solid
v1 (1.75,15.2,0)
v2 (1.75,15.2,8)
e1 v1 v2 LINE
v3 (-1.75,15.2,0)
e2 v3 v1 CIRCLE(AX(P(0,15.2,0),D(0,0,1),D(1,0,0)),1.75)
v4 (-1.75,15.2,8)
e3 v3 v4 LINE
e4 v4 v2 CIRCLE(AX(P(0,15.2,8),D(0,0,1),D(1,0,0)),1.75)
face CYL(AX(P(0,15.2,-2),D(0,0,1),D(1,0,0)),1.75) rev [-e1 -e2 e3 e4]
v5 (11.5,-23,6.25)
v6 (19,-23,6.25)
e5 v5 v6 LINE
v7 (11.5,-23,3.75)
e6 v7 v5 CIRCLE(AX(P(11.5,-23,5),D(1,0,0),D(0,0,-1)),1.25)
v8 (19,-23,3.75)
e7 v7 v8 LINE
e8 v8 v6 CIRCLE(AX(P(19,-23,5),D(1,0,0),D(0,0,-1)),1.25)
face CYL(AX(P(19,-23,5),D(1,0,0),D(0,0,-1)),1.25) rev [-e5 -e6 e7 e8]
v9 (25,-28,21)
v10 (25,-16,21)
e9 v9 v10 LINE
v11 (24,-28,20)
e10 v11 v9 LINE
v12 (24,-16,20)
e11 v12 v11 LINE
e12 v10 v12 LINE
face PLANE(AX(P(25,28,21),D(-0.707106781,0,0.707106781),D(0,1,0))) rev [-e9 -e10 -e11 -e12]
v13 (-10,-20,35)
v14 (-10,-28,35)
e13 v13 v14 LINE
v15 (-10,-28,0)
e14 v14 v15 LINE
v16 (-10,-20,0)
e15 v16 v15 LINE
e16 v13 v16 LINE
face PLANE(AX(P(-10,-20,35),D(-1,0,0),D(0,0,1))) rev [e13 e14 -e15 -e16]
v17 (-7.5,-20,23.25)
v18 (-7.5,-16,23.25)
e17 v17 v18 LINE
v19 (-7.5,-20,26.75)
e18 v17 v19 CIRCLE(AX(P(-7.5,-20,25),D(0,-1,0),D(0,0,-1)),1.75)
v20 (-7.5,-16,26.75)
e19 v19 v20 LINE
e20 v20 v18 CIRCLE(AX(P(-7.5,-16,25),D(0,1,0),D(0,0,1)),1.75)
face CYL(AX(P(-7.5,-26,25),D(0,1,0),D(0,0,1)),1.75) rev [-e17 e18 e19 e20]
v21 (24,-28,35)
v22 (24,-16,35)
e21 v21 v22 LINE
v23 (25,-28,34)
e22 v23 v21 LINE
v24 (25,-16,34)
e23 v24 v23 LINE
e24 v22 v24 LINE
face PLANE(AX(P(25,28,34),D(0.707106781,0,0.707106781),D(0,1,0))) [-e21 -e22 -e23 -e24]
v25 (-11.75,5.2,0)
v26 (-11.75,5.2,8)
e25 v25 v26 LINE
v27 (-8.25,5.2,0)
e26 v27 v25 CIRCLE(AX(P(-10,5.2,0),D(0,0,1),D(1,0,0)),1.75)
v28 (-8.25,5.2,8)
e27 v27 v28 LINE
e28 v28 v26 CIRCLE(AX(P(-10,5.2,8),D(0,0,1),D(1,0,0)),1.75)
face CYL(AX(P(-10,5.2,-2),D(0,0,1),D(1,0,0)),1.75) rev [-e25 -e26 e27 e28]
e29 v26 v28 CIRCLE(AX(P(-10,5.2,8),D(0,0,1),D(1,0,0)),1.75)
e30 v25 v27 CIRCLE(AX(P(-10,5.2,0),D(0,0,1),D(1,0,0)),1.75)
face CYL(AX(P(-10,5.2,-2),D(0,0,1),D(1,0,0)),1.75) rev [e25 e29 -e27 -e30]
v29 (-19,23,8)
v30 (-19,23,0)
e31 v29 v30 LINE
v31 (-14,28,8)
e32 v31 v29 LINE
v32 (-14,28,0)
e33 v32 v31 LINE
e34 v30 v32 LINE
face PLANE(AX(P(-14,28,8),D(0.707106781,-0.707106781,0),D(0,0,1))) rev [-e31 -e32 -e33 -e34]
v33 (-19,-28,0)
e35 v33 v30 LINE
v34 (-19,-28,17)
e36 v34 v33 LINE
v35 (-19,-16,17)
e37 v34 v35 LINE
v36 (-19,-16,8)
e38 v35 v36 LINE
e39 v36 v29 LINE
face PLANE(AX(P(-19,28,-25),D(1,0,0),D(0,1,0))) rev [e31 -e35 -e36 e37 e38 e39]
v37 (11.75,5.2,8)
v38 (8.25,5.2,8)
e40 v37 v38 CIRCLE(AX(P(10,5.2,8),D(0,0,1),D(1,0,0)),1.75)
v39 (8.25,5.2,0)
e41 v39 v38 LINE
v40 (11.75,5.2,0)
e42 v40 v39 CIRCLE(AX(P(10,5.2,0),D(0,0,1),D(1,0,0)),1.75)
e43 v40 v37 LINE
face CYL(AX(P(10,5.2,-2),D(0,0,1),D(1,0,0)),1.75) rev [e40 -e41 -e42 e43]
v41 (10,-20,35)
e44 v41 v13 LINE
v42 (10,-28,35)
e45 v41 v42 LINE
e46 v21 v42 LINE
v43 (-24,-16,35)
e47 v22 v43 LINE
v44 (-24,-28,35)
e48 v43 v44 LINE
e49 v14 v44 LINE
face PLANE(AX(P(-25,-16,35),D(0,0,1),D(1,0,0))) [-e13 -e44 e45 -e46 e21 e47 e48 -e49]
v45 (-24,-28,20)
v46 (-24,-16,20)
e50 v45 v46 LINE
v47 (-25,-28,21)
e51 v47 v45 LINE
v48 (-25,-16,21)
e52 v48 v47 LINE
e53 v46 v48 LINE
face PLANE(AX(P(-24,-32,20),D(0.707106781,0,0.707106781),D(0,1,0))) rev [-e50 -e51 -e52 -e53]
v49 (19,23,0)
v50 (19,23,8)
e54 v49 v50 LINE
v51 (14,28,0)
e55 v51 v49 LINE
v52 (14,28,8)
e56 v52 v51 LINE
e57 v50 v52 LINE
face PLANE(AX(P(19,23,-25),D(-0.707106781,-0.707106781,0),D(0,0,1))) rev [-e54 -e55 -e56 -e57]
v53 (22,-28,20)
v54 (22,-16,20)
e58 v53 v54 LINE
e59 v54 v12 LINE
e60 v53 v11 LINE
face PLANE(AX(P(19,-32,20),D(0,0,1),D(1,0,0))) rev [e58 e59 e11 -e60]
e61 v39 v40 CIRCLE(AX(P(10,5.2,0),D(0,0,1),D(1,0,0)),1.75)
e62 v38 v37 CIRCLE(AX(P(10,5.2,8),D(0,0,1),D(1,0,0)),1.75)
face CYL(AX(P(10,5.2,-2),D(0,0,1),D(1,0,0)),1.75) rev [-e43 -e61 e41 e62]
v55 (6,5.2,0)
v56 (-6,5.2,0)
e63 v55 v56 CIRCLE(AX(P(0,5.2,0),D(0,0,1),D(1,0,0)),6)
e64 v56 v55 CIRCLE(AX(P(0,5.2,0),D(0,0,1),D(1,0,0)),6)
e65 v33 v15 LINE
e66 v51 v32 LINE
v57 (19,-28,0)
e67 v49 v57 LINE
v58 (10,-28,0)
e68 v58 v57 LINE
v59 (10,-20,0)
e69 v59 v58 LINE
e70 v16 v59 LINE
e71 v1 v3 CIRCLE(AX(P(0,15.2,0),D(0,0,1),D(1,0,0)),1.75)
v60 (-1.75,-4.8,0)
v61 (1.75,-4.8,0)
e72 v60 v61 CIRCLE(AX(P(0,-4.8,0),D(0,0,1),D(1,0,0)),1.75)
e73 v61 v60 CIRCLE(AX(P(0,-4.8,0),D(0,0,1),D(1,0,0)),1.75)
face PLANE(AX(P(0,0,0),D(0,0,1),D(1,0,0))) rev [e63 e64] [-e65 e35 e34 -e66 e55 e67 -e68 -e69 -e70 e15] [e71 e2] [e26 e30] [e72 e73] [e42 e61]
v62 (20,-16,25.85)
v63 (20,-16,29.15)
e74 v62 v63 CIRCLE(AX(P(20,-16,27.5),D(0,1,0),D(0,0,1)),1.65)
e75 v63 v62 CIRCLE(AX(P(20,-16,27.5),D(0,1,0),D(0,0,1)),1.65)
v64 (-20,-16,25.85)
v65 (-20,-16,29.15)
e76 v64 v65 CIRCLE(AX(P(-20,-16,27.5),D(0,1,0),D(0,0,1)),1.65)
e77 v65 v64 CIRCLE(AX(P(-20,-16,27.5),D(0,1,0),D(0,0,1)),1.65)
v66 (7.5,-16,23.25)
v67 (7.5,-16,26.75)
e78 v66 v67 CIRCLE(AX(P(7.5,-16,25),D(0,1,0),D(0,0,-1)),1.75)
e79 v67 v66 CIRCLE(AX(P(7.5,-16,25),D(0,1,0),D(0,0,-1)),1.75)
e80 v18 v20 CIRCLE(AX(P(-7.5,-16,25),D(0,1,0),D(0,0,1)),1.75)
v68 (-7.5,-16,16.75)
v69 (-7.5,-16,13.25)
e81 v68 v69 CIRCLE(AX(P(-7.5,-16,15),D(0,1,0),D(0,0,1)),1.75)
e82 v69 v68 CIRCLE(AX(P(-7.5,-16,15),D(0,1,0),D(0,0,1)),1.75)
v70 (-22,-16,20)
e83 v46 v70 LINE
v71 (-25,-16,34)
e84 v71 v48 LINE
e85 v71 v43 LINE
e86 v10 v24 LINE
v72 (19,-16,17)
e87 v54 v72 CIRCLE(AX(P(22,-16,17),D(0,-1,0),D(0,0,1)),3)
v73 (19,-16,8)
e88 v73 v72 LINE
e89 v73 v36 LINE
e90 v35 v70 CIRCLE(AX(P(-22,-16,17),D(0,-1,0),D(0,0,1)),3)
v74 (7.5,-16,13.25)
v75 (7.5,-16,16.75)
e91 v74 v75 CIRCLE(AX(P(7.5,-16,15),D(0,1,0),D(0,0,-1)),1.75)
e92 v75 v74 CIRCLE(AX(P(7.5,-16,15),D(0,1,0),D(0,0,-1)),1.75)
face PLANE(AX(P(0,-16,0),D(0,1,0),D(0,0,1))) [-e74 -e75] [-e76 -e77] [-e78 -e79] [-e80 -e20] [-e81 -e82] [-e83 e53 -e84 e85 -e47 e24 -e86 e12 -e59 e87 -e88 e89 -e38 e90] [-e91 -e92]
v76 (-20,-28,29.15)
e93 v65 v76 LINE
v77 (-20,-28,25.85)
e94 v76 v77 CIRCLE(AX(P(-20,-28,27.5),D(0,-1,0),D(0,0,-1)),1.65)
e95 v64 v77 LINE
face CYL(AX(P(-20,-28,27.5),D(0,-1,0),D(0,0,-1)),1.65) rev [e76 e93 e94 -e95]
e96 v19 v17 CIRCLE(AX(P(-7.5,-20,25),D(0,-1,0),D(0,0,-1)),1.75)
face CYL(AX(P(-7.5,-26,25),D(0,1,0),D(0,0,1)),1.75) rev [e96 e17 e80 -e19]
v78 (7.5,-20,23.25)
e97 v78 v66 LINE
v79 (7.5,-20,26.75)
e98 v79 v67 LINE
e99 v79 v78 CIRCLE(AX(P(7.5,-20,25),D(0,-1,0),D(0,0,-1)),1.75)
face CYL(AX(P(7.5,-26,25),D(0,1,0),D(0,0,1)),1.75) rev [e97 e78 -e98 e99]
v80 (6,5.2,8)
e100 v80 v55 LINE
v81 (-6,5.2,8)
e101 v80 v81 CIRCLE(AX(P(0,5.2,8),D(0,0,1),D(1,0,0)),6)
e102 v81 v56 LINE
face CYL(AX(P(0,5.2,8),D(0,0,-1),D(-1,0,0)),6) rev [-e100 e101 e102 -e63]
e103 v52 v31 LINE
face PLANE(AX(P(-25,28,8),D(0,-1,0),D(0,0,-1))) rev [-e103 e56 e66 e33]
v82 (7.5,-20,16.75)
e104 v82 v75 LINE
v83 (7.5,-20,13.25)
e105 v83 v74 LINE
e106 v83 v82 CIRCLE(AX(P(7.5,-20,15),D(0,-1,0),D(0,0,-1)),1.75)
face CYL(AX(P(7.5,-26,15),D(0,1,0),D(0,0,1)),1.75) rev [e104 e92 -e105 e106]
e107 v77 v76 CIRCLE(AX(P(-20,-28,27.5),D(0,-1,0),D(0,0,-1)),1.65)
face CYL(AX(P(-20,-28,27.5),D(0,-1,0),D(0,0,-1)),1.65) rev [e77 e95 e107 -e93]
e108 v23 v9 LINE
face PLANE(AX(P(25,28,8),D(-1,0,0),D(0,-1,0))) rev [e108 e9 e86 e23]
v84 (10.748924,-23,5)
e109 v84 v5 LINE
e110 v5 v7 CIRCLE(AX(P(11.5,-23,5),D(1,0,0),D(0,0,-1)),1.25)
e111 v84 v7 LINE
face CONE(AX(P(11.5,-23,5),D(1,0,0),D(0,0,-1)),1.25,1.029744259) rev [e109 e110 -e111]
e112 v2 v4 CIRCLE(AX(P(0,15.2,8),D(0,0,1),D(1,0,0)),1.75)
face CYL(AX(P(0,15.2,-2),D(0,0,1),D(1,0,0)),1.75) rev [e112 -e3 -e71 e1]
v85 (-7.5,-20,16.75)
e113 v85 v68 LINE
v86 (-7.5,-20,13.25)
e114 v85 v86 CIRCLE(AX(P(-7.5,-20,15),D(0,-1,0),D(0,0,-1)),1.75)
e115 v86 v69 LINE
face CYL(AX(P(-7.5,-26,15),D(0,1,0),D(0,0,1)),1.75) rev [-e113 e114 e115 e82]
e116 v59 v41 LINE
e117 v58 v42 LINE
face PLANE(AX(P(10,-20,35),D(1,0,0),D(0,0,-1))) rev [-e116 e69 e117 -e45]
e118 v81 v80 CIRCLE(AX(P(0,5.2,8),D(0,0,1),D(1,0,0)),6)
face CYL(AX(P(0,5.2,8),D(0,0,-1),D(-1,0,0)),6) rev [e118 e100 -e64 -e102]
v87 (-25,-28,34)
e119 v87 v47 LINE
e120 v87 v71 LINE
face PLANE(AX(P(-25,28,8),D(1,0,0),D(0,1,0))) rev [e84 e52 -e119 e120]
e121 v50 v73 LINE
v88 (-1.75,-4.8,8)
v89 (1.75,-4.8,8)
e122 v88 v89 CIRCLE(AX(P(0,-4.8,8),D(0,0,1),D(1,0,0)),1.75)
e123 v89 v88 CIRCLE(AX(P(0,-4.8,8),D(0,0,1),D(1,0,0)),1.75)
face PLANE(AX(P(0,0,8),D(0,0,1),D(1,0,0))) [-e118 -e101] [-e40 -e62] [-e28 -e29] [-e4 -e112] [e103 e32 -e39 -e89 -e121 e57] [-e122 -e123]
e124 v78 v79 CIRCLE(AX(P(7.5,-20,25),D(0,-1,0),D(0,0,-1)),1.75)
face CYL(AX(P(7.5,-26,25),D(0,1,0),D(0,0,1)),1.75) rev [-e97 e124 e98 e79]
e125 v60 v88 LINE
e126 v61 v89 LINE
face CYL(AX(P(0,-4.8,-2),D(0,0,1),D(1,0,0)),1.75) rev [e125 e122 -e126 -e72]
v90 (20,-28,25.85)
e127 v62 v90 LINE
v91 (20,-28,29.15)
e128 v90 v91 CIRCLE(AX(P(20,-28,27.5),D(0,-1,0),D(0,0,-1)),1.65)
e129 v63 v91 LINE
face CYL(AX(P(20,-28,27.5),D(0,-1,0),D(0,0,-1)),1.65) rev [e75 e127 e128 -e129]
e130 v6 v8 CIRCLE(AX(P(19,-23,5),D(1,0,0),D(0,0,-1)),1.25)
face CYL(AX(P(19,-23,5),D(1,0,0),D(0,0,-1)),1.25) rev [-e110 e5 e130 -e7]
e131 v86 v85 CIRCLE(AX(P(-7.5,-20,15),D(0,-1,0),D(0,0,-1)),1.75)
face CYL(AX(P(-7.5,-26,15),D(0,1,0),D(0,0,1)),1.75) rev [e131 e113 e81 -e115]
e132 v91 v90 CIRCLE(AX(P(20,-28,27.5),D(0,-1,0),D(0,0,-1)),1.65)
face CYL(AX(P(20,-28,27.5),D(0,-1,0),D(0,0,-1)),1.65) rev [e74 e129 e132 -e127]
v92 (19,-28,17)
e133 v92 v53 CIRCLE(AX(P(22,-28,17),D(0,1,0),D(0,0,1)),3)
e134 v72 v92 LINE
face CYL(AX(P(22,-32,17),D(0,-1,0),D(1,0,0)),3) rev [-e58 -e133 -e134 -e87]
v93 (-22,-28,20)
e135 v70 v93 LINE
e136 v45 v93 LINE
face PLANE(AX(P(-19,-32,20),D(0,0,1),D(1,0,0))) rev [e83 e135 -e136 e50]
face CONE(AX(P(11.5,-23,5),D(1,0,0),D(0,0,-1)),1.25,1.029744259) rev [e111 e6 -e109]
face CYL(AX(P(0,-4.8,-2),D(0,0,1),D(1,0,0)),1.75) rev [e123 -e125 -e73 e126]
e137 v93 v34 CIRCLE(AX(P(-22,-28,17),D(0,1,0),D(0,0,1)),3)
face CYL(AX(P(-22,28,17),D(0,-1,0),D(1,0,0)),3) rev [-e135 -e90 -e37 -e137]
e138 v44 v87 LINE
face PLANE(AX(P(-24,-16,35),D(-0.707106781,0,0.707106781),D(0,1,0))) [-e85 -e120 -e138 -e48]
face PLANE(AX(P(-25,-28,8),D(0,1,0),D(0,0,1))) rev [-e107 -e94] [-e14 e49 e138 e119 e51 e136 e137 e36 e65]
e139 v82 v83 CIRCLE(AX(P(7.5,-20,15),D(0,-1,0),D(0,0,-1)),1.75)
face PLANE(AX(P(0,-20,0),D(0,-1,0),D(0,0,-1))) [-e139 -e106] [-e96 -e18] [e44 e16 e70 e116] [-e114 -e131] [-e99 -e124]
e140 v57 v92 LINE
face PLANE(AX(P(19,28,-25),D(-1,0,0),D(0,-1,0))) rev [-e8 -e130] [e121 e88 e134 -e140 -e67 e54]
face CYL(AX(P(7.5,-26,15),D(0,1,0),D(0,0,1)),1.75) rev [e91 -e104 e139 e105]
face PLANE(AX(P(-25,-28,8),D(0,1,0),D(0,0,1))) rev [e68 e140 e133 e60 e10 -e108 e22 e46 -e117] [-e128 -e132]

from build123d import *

# Parameters (mm, degrees)
SKETCH1_W             = 50
SKETCH1_H             = 56
SKETCH1_R             = 6
BOSS_EXTRUDE1_DEPTH   = 8
SKETCH2_W             = 50
SKETCH2_H             = 35
BOSS_EXTRUDE2_DEPTH   = 12
SKETCH3_W             = 20
SKETCH3_H             = 35
CUT_EXTRUDE1_DEPTH    = 8
SKETCH4_W             = 6
SKETCH4_H             = 44
CUT_EXTRUDE2_DEPTH    = 60
CHAMFER2_SIZE         = 5
SKETCH5_W             = 6
SKETCH5_H             = 20
CUT_EXTRUDE3_DEPTH    = 60
M4_TAPPED_HOLE1_D     = 3.3
FILLET1_R             = 3
SKETCH9_R             = 1.75
CUT_EXTRUDE4_DEPTH    = 10
SKETCH10_R            = 1.75
CUT_EXTRUDE5_DEPTH    = 10
M3_TAPPED_HOLE1_D     = 2.5
M3_TAPPED_HOLE1_DEPTH = 7.5
M3_TAPPED_HOLE1_TIP   = 0.751075774
CHAMFER3_SIZE         = 1


with BuildPart() as part:
    # Sketch1 → Boss-Extrude1 (new body)
    with BuildSketch(Plane.XY):
        Rectangle(SKETCH1_W, SKETCH1_H)
        with Locations((0, 5.2)):
            Circle(SKETCH1_R, mode=Mode.SUBTRACT)
    extrude(amount=BOSS_EXTRUDE1_DEPTH)

    # Sketch2 → Boss-Extrude2 (add)
    with BuildSketch(Plane.XZ.offset(28)):
        with Locations((0, 17.5)):
            Rectangle(SKETCH2_W, SKETCH2_H)
    extrude(amount=-BOSS_EXTRUDE2_DEPTH)

    # Sketch3 → Cut-Extrude1 (cut)
    with BuildSketch(Plane.XZ.offset(28)):
        with Locations((0, 17.5)):
            Rectangle(SKETCH3_W, SKETCH3_H)
    extrude(amount=-CUT_EXTRUDE1_DEPTH, mode=Mode.SUBTRACT)

    # Sketch4 → Cut-Extrude2 (cut)
    with BuildSketch(Plane.XY.offset(35)):
        with Locations((-22, 6)):
            Rectangle(SKETCH4_W, SKETCH4_H)
        with Locations((22, 6)):
            Rectangle(SKETCH4_W, SKETCH4_H)
    extrude(amount=-CUT_EXTRUDE2_DEPTH, mode=Mode.SUBTRACT)

    # Chamfer2
    chamfer2_edges = [part.edges().sort_by_distance(p)[0] for p in [
        (-19, 28, 4),
        (19, 28, 4),
    ]]
    chamfer(chamfer2_edges, length=CHAMFER2_SIZE)

    # Sketch5 → Cut-Extrude3 (cut)
    with BuildSketch(Plane(origin=(0, 28, 0), x_dir=(1, 0, 0), z_dir=(0, 1, 0))):
        with Locations((-22, -10)):
            Rectangle(SKETCH5_W, SKETCH5_H)
        with Locations((22, -10)):
            Rectangle(SKETCH5_W, SKETCH5_H)
    extrude(amount=-CUT_EXTRUDE3_DEPTH, mode=Mode.SUBTRACT)

    # M4 Tapped Hole1 (through all)
    with Locations(Plane(origin=(0, -28, 0), x_dir=(-1, 0, 0), z_dir=(0, -1, 0))):
        with Locations((20, -27.5), (-20, -27.5)):
            Hole(M4_TAPPED_HOLE1_D / 2)

    # Fillet1
    fillet1_edges = [part.edges().sort_by_distance(p)[0] for p in [
        (-19, -22, 20),
        (19, -22, 20),
    ]]
    fillet(fillet1_edges, radius=FILLET1_R)

    # Sketch9 → Cut-Extrude4 (cut)
    with BuildSketch(Plane(origin=(0, -16, 0), x_dir=(1, 0, 0), z_dir=(0, 1, 0))):
        with Locations(Location((-7.5, -15, 0), (0, 0, 270))):
            Circle(SKETCH9_R)
        with Locations(Location((7.5, -15, 0), (0, 0, 90))):
            Circle(SKETCH9_R)
        with Locations(Location((-7.5, -25, 0), (0, 0, 270))):
            Circle(SKETCH9_R)
        with Locations(Location((7.5, -25, 0), (0, 0, 90))):
            Circle(SKETCH9_R)
    extrude(amount=-CUT_EXTRUDE4_DEPTH, mode=Mode.SUBTRACT)

    # Sketch10 → Cut-Extrude5 (cut)
    with BuildSketch(Plane.XY.offset(8)):
        with Locations((10, 5.2)):
            Circle(SKETCH10_R)
        with Locations((0, 15.2)):
            Circle(SKETCH10_R)
        with Locations((-10, 5.2)):
            Circle(SKETCH10_R)
        with Locations((0, -4.8)):
            Circle(SKETCH10_R)
    extrude(amount=-CUT_EXTRUDE5_DEPTH, mode=Mode.SUBTRACT)

    # M3 Tapped Hole1
    with Locations(Plane(origin=(19, 0, 0), x_dir=(0, 0, -1), z_dir=(1, 0, 0))):
        with Locations((-5, -23)):
            Hole(M3_TAPPED_HOLE1_D / 2, depth=M3_TAPPED_HOLE1_DEPTH)
            with Locations((0, 0, -(M3_TAPPED_HOLE1_DEPTH + M3_TAPPED_HOLE1_TIP / 2))):  # 118° drill point
                Cone(0, M3_TAPPED_HOLE1_D / 2, M3_TAPPED_HOLE1_TIP, mode=Mode.SUBTRACT)

    # Chamfer3
    chamfer3_edges = [part.edges().sort_by_distance(p)[0] for p in [
        (-25, -22, 20),
        (25, -22, 20),
        (-25, -22, 35),
        (25, -22, 35),
    ]]
    chamfer(chamfer3_edges, length=CHAMFER3_SIZE)


solid = part.part
